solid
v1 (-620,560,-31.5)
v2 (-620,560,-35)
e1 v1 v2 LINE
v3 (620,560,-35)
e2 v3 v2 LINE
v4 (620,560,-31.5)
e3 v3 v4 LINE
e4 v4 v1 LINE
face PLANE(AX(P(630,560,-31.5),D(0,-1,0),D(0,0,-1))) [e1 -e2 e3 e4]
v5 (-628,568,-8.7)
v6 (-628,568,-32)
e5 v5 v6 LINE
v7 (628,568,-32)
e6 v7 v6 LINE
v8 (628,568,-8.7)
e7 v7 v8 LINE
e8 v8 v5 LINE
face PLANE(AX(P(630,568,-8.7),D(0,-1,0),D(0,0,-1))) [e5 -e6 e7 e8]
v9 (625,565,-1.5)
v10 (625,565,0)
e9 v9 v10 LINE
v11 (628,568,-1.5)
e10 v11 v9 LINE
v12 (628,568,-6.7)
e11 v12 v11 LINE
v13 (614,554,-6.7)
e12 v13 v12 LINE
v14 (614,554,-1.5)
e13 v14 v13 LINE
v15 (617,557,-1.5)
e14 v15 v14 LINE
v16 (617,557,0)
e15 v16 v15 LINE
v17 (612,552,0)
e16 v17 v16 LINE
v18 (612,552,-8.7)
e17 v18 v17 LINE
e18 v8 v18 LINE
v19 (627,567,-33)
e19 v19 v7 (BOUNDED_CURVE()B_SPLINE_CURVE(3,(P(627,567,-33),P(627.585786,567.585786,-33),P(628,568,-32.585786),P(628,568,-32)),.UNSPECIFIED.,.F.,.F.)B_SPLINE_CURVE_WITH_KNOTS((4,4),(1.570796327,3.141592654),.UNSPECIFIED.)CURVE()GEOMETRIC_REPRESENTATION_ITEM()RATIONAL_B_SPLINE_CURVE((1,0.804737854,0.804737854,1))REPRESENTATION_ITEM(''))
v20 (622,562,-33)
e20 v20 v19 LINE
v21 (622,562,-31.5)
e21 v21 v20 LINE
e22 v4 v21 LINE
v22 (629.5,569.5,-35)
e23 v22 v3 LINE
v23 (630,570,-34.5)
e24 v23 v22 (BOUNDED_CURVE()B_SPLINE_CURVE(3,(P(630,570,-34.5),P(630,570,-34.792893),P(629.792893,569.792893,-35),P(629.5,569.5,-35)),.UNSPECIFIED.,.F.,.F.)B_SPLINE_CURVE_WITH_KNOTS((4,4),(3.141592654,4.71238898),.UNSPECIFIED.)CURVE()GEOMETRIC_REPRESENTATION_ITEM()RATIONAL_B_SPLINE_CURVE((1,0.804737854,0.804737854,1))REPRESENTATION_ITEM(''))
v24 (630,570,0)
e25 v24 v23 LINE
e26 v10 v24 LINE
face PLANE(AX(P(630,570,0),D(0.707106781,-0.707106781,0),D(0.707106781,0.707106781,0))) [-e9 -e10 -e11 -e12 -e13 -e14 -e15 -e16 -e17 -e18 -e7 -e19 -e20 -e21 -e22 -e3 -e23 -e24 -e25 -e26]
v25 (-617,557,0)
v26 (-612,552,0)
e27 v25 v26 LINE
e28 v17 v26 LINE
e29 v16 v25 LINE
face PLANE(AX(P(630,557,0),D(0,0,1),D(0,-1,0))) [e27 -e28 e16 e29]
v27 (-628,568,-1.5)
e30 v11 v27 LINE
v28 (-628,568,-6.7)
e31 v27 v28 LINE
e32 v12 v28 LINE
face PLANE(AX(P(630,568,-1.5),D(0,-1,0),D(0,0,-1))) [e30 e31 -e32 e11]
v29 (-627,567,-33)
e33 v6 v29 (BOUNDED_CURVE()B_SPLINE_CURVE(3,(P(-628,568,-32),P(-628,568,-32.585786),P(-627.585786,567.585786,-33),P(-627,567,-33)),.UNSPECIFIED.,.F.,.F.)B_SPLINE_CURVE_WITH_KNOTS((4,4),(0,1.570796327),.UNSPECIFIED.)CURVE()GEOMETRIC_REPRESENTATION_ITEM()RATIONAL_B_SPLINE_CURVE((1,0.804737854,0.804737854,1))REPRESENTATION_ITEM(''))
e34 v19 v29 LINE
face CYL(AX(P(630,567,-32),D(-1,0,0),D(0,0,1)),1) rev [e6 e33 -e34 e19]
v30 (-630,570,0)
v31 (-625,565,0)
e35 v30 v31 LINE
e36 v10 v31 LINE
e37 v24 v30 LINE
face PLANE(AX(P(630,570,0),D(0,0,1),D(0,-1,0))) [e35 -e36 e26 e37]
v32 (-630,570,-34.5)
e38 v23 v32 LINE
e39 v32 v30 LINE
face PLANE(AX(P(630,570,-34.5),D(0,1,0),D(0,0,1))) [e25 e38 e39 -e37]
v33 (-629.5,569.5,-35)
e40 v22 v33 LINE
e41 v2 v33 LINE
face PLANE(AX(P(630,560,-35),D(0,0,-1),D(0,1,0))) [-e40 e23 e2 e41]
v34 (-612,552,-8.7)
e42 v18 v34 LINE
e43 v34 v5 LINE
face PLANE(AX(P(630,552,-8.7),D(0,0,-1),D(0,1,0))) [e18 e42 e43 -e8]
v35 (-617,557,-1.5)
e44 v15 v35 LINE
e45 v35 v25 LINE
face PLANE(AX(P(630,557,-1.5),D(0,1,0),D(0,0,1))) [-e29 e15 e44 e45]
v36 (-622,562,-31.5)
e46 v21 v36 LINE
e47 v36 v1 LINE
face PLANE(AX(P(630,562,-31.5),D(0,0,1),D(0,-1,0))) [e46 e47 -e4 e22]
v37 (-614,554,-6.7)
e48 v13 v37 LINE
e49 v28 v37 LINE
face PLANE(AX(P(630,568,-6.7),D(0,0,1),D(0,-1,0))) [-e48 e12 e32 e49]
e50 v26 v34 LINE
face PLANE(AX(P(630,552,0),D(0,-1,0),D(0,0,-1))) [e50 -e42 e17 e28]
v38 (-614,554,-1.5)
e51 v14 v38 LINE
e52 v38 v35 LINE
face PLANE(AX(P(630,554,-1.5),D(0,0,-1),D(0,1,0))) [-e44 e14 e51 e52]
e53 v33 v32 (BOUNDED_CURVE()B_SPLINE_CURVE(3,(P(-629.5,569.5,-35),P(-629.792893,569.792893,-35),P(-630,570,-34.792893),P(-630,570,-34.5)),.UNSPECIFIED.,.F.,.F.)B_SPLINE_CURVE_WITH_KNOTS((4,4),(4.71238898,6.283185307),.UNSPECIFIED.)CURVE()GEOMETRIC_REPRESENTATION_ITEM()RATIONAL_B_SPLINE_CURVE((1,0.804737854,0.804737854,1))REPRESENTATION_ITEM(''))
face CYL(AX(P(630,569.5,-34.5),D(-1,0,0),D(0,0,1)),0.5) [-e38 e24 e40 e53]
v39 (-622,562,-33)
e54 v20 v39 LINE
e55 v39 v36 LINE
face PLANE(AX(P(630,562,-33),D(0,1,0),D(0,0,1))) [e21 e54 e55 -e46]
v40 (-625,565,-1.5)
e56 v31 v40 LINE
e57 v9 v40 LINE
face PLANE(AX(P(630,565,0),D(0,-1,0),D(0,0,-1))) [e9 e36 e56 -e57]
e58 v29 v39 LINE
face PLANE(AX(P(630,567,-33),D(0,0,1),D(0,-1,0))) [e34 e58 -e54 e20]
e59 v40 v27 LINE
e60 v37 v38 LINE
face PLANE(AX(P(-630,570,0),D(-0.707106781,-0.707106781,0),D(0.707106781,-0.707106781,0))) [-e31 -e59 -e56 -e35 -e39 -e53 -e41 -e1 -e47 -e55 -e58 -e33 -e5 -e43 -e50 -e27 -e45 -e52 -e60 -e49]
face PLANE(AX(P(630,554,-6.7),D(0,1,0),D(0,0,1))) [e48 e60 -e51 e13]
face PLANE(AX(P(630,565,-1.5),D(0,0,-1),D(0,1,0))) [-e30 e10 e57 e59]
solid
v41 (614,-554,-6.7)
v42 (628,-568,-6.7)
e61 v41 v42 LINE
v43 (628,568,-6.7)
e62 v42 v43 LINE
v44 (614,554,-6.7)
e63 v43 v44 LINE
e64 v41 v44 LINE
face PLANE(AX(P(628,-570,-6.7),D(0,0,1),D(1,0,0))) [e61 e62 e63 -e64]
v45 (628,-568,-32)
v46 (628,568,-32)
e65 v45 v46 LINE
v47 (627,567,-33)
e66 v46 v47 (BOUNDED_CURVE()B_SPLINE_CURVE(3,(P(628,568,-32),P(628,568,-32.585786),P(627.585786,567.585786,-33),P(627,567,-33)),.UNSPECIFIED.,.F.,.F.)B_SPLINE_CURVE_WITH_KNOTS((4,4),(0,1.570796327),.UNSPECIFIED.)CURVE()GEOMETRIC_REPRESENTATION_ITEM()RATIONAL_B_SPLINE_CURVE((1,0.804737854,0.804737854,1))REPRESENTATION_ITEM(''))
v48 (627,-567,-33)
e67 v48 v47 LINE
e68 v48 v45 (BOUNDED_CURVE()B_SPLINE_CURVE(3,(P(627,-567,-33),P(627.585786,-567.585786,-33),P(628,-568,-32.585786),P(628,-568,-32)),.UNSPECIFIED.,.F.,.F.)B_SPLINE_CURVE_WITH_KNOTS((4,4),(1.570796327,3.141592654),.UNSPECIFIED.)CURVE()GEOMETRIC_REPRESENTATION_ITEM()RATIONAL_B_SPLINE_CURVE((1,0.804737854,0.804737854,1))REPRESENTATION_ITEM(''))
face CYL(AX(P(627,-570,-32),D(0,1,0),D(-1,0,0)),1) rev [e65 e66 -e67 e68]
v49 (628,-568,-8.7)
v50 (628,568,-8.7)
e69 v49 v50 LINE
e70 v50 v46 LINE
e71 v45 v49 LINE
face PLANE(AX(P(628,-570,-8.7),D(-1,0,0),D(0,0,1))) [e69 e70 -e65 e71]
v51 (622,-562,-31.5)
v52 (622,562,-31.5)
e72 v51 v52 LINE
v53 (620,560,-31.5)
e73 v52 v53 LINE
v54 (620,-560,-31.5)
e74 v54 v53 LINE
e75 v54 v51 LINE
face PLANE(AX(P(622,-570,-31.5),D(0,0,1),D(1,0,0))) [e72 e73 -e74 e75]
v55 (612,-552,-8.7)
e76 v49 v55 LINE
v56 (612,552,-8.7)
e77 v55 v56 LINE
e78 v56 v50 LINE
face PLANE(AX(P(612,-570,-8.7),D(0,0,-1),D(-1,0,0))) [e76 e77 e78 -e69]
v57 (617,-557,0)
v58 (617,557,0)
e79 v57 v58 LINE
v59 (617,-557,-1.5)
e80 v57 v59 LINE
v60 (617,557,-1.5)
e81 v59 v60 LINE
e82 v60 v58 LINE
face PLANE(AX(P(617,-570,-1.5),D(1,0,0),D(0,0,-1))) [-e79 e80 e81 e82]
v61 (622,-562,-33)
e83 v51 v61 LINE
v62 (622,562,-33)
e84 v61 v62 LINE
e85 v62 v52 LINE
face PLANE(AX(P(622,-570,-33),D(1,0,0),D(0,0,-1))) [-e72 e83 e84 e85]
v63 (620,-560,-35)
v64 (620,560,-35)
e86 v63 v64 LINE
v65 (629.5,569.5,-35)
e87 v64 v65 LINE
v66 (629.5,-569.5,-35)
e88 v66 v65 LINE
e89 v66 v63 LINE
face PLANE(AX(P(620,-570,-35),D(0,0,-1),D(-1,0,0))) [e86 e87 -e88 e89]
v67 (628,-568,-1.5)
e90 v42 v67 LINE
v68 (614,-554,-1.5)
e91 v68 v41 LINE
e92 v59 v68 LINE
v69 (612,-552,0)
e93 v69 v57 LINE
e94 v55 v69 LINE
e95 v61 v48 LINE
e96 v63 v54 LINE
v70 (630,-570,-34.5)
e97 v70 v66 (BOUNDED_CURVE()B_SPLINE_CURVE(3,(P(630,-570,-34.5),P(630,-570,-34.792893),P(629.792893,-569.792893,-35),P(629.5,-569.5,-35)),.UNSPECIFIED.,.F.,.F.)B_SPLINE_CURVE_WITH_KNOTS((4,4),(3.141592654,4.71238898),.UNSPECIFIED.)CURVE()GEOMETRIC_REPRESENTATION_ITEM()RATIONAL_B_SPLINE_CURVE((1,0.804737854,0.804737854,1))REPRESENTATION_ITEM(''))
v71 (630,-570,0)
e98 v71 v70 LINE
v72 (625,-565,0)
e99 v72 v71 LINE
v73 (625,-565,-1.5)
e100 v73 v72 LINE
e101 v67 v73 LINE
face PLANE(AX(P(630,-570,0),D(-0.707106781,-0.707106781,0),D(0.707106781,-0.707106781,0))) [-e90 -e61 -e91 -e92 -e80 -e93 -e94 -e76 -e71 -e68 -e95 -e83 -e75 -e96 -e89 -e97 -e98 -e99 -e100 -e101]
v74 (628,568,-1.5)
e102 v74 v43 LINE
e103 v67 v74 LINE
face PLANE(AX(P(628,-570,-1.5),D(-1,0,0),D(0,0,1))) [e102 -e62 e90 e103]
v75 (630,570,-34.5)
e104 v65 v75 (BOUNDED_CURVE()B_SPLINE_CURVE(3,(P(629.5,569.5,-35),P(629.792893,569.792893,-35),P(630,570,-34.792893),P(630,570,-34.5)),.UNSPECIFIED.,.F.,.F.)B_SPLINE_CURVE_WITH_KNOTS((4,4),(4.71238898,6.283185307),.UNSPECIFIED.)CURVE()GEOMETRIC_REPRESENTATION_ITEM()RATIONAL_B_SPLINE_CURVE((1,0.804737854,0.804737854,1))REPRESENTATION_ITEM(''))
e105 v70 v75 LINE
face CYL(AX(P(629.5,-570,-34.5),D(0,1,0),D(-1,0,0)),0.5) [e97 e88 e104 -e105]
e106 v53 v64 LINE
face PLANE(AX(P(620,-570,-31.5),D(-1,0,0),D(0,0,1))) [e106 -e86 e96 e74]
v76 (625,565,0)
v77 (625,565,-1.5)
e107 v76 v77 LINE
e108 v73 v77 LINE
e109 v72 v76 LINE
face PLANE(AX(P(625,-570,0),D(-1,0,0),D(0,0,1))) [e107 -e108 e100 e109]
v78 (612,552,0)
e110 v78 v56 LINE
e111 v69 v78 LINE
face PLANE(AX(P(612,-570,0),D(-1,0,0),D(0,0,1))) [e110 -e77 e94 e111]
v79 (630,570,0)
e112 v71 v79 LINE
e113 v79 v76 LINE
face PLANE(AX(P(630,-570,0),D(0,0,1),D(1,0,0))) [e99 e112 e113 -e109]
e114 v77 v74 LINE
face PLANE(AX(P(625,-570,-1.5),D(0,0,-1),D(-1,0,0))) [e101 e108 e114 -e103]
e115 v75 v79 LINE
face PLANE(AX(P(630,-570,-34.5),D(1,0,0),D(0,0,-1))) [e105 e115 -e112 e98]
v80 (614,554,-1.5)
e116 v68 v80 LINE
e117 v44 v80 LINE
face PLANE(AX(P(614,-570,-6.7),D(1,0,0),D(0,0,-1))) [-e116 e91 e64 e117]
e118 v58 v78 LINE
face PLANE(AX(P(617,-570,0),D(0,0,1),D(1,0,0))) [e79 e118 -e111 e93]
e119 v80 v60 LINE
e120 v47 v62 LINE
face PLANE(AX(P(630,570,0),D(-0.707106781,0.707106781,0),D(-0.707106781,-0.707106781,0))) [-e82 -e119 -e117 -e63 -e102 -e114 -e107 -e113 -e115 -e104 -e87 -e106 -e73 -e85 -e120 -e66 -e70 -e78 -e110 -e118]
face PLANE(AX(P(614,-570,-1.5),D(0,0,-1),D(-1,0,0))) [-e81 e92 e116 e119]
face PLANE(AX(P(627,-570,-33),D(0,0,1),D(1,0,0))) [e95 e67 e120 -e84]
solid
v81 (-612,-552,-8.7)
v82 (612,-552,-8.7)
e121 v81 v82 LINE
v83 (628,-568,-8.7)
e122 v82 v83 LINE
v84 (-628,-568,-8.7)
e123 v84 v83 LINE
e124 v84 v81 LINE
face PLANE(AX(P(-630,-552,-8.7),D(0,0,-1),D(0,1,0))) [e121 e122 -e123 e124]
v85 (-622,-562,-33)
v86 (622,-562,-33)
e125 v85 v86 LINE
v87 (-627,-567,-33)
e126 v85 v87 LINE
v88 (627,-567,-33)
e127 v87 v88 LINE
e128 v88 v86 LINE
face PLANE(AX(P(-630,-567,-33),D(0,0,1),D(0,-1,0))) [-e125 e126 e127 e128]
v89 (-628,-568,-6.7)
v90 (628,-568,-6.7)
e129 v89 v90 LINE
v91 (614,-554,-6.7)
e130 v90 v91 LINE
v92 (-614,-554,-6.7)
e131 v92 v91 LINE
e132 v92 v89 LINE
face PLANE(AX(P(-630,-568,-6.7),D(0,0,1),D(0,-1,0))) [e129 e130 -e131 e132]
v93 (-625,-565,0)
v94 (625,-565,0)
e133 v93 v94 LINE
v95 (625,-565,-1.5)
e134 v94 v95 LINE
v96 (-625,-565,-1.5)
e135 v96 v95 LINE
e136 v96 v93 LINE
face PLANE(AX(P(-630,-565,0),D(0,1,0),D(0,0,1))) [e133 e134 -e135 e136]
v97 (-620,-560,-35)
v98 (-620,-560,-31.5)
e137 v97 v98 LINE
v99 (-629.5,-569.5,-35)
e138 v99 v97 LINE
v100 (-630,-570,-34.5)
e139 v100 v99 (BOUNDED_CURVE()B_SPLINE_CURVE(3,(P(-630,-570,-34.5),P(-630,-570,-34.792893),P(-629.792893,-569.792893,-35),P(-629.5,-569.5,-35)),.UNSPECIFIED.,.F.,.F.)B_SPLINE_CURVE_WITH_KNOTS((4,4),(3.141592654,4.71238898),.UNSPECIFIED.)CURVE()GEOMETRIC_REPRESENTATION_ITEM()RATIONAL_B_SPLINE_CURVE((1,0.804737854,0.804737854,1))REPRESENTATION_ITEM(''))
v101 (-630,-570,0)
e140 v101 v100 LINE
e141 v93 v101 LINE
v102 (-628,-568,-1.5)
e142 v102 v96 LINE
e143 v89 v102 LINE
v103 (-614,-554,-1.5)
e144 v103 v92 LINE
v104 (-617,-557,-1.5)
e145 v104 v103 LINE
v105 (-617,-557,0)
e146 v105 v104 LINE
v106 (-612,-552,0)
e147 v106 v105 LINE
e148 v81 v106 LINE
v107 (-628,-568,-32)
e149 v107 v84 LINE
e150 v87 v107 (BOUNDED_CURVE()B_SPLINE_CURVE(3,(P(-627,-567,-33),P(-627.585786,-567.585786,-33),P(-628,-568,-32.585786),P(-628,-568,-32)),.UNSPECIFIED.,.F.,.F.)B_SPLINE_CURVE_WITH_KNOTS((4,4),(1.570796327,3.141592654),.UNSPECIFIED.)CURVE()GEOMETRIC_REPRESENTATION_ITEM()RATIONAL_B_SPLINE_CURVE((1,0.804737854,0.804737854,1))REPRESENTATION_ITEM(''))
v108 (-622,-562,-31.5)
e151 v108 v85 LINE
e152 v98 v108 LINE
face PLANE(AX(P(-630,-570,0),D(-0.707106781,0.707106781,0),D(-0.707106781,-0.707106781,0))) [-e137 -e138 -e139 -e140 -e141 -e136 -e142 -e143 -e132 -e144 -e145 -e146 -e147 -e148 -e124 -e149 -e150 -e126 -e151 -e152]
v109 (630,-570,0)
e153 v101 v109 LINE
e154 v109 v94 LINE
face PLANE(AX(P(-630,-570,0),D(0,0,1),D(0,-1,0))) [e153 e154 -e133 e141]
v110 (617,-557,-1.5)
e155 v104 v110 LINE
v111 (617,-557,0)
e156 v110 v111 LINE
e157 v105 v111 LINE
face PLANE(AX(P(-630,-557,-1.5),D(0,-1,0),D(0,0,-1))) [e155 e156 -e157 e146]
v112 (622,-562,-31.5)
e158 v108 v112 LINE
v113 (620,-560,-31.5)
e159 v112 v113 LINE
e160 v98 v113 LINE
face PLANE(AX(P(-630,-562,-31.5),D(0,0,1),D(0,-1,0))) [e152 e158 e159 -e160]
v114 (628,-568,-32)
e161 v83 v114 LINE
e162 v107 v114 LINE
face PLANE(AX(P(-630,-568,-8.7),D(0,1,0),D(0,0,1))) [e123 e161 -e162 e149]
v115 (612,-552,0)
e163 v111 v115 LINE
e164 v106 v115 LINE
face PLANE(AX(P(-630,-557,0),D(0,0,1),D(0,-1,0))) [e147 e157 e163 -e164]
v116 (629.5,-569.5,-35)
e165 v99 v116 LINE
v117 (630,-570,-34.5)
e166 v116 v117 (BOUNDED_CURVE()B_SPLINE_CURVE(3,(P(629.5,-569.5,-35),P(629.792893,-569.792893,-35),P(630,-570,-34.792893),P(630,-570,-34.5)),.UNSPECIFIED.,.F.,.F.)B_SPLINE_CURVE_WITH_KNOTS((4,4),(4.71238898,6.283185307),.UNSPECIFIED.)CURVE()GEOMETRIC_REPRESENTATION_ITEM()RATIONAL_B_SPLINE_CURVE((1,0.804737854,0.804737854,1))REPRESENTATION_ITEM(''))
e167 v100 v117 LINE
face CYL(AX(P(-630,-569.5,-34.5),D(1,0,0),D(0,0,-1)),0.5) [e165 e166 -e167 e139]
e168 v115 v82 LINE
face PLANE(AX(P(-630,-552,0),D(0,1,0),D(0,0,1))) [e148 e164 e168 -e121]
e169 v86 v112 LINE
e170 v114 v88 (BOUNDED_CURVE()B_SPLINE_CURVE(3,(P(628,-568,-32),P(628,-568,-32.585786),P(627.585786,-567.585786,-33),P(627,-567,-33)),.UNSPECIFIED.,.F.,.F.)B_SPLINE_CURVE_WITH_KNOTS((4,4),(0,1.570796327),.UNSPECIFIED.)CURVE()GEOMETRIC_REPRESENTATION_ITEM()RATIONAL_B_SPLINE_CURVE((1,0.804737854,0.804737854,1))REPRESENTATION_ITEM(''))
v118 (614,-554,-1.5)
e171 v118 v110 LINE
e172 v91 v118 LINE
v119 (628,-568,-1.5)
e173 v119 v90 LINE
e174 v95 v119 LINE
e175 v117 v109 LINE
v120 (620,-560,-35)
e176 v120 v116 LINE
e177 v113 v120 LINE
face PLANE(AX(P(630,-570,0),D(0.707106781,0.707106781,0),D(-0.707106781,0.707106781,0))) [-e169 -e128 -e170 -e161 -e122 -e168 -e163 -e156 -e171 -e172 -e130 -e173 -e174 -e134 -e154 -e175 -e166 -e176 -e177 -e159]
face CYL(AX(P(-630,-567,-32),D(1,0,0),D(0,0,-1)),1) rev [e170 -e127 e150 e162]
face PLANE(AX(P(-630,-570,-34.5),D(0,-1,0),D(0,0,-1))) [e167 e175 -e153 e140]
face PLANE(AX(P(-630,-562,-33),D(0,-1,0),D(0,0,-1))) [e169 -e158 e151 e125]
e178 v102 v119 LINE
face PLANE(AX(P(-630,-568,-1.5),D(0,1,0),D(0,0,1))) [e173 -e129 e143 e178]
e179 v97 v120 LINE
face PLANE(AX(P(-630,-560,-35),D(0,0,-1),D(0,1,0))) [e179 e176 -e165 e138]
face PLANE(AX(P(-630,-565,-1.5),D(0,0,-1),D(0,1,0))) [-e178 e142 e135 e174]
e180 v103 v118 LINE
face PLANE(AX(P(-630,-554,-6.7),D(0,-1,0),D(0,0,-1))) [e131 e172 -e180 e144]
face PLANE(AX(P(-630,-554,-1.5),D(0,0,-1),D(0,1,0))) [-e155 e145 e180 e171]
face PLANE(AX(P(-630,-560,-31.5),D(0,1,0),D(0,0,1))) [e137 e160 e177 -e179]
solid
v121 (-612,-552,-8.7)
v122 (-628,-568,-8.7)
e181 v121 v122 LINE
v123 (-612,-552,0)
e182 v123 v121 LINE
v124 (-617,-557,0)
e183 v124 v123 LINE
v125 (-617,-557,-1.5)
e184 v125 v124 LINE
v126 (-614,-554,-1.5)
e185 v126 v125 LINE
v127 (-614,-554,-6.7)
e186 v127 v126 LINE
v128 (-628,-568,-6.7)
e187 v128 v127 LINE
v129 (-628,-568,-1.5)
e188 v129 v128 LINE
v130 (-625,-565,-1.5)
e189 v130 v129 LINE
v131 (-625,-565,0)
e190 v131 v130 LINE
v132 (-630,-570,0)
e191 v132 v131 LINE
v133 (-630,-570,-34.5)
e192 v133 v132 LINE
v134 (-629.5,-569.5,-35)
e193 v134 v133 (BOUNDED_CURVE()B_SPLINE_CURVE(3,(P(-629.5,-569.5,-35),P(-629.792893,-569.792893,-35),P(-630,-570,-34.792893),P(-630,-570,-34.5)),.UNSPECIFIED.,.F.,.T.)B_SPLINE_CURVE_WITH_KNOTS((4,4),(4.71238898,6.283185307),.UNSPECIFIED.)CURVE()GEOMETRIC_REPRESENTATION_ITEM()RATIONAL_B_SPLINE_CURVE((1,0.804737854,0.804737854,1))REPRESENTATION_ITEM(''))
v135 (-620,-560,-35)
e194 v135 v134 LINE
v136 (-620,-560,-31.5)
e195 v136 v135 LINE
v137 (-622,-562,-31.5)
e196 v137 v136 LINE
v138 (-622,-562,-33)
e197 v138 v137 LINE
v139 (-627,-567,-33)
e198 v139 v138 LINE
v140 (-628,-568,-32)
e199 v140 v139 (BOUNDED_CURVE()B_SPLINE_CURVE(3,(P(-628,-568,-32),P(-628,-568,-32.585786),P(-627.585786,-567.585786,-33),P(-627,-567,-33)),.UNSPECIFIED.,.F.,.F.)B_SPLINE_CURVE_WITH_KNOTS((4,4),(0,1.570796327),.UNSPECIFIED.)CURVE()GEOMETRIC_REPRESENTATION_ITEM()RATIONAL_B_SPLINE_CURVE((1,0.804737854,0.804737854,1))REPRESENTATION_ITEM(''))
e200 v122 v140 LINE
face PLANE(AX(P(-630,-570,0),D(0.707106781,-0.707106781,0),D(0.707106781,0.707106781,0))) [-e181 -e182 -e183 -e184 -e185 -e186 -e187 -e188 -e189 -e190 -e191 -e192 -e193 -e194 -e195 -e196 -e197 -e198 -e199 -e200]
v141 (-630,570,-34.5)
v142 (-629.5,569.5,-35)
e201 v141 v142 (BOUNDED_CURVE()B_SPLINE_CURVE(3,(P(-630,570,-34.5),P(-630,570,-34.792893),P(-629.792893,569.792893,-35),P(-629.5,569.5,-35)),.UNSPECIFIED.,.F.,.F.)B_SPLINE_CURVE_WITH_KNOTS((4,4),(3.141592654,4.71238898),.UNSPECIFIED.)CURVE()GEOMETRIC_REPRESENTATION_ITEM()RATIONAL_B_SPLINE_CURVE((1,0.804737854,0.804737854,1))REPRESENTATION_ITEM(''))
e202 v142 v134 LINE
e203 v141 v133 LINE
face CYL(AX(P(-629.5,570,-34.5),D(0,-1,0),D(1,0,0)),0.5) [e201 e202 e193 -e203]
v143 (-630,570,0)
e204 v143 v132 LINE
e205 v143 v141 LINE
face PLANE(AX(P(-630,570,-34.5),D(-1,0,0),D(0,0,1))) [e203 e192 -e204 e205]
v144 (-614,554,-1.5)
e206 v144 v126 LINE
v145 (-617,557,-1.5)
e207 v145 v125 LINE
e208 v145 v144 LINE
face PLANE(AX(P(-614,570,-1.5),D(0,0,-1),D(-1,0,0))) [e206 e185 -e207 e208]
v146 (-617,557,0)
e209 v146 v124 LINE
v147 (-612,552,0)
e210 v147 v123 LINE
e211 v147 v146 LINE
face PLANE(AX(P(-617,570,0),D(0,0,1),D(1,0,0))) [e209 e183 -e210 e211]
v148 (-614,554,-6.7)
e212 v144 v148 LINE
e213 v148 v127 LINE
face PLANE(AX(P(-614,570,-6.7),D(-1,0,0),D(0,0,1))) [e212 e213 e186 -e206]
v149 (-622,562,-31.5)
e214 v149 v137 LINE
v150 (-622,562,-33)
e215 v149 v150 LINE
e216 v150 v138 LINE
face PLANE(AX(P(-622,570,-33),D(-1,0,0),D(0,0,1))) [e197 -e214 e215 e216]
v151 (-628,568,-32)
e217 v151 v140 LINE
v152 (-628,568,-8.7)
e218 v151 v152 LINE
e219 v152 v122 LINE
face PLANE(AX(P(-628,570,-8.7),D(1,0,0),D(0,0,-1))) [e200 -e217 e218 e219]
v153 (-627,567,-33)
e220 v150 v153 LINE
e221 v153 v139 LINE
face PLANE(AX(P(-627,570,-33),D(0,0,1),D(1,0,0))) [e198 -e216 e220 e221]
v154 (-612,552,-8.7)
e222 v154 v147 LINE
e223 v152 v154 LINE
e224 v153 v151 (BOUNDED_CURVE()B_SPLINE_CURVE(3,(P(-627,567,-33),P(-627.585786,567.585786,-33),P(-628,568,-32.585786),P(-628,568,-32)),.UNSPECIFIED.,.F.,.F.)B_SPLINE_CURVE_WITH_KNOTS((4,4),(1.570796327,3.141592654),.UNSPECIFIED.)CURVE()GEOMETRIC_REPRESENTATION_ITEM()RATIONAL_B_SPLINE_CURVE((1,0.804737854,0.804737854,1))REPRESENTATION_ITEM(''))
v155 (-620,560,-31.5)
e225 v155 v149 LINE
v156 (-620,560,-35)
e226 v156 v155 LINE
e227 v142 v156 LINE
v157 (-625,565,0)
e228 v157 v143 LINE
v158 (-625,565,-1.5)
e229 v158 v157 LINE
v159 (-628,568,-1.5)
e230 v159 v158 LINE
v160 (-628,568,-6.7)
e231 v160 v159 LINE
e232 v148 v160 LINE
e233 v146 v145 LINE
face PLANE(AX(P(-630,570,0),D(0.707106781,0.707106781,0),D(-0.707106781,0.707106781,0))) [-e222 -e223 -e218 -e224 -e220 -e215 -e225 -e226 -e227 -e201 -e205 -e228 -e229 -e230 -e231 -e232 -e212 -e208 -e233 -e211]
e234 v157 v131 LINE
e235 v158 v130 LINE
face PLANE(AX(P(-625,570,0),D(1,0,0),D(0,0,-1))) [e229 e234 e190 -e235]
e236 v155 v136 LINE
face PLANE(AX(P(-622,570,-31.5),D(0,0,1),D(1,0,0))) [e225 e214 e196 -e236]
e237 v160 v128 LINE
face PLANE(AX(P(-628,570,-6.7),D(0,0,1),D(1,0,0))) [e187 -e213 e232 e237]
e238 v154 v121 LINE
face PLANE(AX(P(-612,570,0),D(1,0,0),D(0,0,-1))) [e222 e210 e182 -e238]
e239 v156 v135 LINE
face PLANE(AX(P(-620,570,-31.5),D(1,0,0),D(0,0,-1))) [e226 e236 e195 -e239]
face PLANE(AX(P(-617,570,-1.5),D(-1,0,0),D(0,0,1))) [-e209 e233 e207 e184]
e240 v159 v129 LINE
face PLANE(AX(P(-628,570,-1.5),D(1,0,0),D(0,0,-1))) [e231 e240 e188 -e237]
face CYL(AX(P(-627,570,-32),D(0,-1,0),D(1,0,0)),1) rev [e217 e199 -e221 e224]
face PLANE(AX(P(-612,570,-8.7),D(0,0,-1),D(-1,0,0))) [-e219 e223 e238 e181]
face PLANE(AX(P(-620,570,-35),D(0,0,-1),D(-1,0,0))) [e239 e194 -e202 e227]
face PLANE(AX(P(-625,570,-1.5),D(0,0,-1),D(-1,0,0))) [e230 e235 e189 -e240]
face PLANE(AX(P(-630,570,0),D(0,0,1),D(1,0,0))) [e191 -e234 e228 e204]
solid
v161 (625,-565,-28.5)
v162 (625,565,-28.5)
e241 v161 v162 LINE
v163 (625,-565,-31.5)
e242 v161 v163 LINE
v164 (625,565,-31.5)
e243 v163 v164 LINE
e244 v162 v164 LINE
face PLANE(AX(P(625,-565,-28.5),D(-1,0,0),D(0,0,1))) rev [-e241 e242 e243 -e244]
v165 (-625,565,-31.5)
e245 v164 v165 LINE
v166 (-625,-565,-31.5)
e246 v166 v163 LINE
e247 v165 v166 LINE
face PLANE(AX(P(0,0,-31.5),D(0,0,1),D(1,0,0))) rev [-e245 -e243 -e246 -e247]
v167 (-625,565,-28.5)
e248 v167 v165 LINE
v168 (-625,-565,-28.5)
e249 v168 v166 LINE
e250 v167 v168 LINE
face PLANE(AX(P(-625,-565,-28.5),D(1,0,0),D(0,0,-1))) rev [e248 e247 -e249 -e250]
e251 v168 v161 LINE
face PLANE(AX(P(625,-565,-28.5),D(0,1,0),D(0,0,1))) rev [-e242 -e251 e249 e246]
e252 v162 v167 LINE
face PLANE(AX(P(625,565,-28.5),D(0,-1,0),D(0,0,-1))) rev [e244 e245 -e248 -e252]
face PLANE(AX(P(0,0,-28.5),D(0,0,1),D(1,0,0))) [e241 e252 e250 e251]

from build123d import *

# Parameters (mm, degrees)
MEMBER_1_DEPTH      = 40.357337308
MEMBER_1_DEPTH_BACK = 1300.357337308
MEMBER_1_2_DEPTH    = 1220.714674617
MEMBER_1_3_DEPTH    = 1340.714674617
MEMBER_1_4_DEPTH    = 1220.714674617
SKETCH_12_W         = 1250
SKETCH_12_H         = 1130
EXTRUDE_1_DEPTH     = 3


with BuildPart() as part:
    # 草图11 → Member 1 (new, two sides: drawn at the far end of the back side and taken through both)
    with BuildSketch(Plane(origin=(-630, 570, 0), x_dir=(0, -1, 0), z_dir=(-1, 0, 0)).offset(-MEMBER_1_DEPTH_BACK)):
        with BuildLine():
            Line((13, -1.5), (13, 0))
            Line((13, 0), (18, 0))
            Line((18, 0), (18, -8.7))
            Line((18, -8.7), (2, -8.7))
            Line((2, -8.7), (2, -32))
            ThreePointArc((2, -32), (2.292893219, -32.707106781), (3, -33))
            Line((3, -33), (8, -33))
            Line((8, -33), (8, -31.5))
            Line((8, -31.5), (10, -31.5))
            Line((10, -31.5), (10, -35))
            Line((10, -35), (0.5, -35))
            ThreePointArc((0.5, -35), (0.146446609, -34.853553391), (0, -34.5))
            Line((0, -34.5), (0, 0))
            Line((0, 0), (5, 0))
            Line((5, 0), (5, -1.5))
            Line((5, -1.5), (2, -1.5))
            Line((2, -1.5), (2, -6.7))
            Line((2, -6.7), (16, -6.7))
            Line((16, -6.7), (16, -1.5))
            Line((16, -1.5), (13, -1.5))
        make_face()
    extrude(amount=MEMBER_1_DEPTH + MEMBER_1_DEPTH_BACK)

    # Member 1 mitre 1
    split(bisect_by=Plane(origin=(-630, 570, 0), x_dir=(-0.707106781, 0.707106781, 0), z_dir=(0.707106781, 0.707106781, 0)), keep=Keep.TOP)

    # Member 1 mitre 2
    split(bisect_by=Plane(origin=(630, 570, 0), x_dir=(-0.707106781, -0.707106781, 0), z_dir=(-0.707106781, 0.707106781, 0)), keep=Keep.TOP)


with BuildPart() as body_2:
    # 草图11 on segment 2 (carried to segment 2) → Member 1 2 (new body)
    with BuildSketch(Plane(origin=(630, -610.357337308, 0), x_dir=(-1, 0, 0), z_dir=(0, 1, 0))):
        with BuildLine():
            Line((13, -1.5), (13, 0))
            Line((13, 0), (18, 0))
            Line((18, 0), (18, -8.7))
            Line((18, -8.7), (2, -8.7))
            Line((2, -8.7), (2, -32))
            ThreePointArc((2, -32), (2.292893219, -32.707106781), (3, -33))
            Line((3, -33), (8, -33))
            Line((8, -33), (8, -31.5))
            Line((8, -31.5), (10, -31.5))
            Line((10, -31.5), (10, -35))
            Line((10, -35), (0.5, -35))
            ThreePointArc((0.5, -35), (0.146446609, -34.853553391), (0, -34.5))
            Line((0, -34.5), (0, 0))
            Line((0, 0), (5, 0))
            Line((5, 0), (5, -1.5))
            Line((5, -1.5), (2, -1.5))
            Line((2, -1.5), (2, -6.7))
            Line((2, -6.7), (16, -6.7))
            Line((16, -6.7), (16, -1.5))
            Line((16, -1.5), (13, -1.5))
        make_face()
    extrude(amount=MEMBER_1_2_DEPTH)

    # Member 1 2 mitre 1
    split(bisect_by=Plane(origin=(630, 570, 0), x_dir=(0.707106781, 0.707106781, 0), z_dir=(0.707106781, -0.707106781, 0)), keep=Keep.TOP)

    # Member 1 2 mitre 2
    split(bisect_by=Plane(origin=(630, -570, 0), x_dir=(-0.707106781, 0.707106781, 0), z_dir=(0.707106781, 0.707106781, 0)), keep=Keep.TOP)


with BuildPart() as body_3:
    # 草图11 on segment 3 (carried to segment 3) → Member 1 3 (new body)
    with BuildSketch(Plane(origin=(-670.357337308, -570, 0), x_dir=(0, 1, 0), z_dir=(1, 0, 0))):
        with BuildLine():
            Line((13, -1.5), (13, 0))
            Line((13, 0), (18, 0))
            Line((18, 0), (18, -8.7))
            Line((18, -8.7), (2, -8.7))
            Line((2, -8.7), (2, -32))
            ThreePointArc((2, -32), (2.292893219, -32.707106781), (3, -33))
            Line((3, -33), (8, -33))
            Line((8, -33), (8, -31.5))
            Line((8, -31.5), (10, -31.5))
            Line((10, -31.5), (10, -35))
            Line((10, -35), (0.5, -35))
            ThreePointArc((0.5, -35), (0.146446609, -34.853553391), (0, -34.5))
            Line((0, -34.5), (0, 0))
            Line((0, 0), (5, 0))
            Line((5, 0), (5, -1.5))
            Line((5, -1.5), (2, -1.5))
            Line((2, -1.5), (2, -6.7))
            Line((2, -6.7), (16, -6.7))
            Line((16, -6.7), (16, -1.5))
            Line((16, -1.5), (13, -1.5))
        make_face()
    extrude(amount=MEMBER_1_3_DEPTH)

    # Member 1 3 mitre 1
    split(bisect_by=Plane(origin=(-630, -570, 0), x_dir=(0.707106781, 0.707106781, 0), z_dir=(0.707106781, -0.707106781, 0)), keep=Keep.TOP)

    # Member 1 3 mitre 2
    split(bisect_by=Plane(origin=(630, -570, 0), x_dir=(0.707106781, -0.707106781, 0), z_dir=(-0.707106781, -0.707106781, 0)), keep=Keep.TOP)


with BuildPart() as body_4:
    # 草图11 on segment 4 (carried to segment 4) → Member 1 4 (new body)
    with BuildSketch(Plane(origin=(-630, 610.357337308, 0), x_dir=(1, 0, 0), z_dir=(0, -1, 0))):
        with BuildLine():
            Line((13, -1.5), (13, 0))
            Line((13, 0), (18, 0))
            Line((18, 0), (18, -8.7))
            Line((18, -8.7), (2, -8.7))
            Line((2, -8.7), (2, -32))
            ThreePointArc((2, -32), (2.292893219, -32.707106781), (3, -33))
            Line((3, -33), (8, -33))
            Line((8, -33), (8, -31.5))
            Line((8, -31.5), (10, -31.5))
            Line((10, -31.5), (10, -35))
            Line((10, -35), (0.5, -35))
            ThreePointArc((0.5, -35), (0.146446609, -34.853553391), (0, -34.5))
            Line((0, -34.5), (0, 0))
            Line((0, 0), (5, 0))
            Line((5, 0), (5, -1.5))
            Line((5, -1.5), (2, -1.5))
            Line((2, -1.5), (2, -6.7))
            Line((2, -6.7), (16, -6.7))
            Line((16, -6.7), (16, -1.5))
            Line((16, -1.5), (13, -1.5))
        make_face()
    extrude(amount=MEMBER_1_4_DEPTH)

    # Member 1 4 mitre 1
    split(bisect_by=Plane(origin=(-630, 570, 0), x_dir=(0.707106781, -0.707106781, 0), z_dir=(-0.707106781, -0.707106781, 0)), keep=Keep.TOP)

    # Member 1 4 mitre 2
    split(bisect_by=Plane(origin=(-630, -570, 0), x_dir=(-0.707106781, -0.707106781, 0), z_dir=(-0.707106781, 0.707106781, 0)), keep=Keep.TOP)


with BuildPart() as body_5:
    # 草图12 → 凸台-拉伸1 (new body)
    with BuildSketch(Plane.XY.offset(-31.5)):
        Rectangle(SKETCH_12_W, SKETCH_12_H)
    extrude(amount=EXTRUDE_1_DEPTH)


solid = Compound([part.part, body_2.part, body_3.part, body_4.part, body_5.part])
